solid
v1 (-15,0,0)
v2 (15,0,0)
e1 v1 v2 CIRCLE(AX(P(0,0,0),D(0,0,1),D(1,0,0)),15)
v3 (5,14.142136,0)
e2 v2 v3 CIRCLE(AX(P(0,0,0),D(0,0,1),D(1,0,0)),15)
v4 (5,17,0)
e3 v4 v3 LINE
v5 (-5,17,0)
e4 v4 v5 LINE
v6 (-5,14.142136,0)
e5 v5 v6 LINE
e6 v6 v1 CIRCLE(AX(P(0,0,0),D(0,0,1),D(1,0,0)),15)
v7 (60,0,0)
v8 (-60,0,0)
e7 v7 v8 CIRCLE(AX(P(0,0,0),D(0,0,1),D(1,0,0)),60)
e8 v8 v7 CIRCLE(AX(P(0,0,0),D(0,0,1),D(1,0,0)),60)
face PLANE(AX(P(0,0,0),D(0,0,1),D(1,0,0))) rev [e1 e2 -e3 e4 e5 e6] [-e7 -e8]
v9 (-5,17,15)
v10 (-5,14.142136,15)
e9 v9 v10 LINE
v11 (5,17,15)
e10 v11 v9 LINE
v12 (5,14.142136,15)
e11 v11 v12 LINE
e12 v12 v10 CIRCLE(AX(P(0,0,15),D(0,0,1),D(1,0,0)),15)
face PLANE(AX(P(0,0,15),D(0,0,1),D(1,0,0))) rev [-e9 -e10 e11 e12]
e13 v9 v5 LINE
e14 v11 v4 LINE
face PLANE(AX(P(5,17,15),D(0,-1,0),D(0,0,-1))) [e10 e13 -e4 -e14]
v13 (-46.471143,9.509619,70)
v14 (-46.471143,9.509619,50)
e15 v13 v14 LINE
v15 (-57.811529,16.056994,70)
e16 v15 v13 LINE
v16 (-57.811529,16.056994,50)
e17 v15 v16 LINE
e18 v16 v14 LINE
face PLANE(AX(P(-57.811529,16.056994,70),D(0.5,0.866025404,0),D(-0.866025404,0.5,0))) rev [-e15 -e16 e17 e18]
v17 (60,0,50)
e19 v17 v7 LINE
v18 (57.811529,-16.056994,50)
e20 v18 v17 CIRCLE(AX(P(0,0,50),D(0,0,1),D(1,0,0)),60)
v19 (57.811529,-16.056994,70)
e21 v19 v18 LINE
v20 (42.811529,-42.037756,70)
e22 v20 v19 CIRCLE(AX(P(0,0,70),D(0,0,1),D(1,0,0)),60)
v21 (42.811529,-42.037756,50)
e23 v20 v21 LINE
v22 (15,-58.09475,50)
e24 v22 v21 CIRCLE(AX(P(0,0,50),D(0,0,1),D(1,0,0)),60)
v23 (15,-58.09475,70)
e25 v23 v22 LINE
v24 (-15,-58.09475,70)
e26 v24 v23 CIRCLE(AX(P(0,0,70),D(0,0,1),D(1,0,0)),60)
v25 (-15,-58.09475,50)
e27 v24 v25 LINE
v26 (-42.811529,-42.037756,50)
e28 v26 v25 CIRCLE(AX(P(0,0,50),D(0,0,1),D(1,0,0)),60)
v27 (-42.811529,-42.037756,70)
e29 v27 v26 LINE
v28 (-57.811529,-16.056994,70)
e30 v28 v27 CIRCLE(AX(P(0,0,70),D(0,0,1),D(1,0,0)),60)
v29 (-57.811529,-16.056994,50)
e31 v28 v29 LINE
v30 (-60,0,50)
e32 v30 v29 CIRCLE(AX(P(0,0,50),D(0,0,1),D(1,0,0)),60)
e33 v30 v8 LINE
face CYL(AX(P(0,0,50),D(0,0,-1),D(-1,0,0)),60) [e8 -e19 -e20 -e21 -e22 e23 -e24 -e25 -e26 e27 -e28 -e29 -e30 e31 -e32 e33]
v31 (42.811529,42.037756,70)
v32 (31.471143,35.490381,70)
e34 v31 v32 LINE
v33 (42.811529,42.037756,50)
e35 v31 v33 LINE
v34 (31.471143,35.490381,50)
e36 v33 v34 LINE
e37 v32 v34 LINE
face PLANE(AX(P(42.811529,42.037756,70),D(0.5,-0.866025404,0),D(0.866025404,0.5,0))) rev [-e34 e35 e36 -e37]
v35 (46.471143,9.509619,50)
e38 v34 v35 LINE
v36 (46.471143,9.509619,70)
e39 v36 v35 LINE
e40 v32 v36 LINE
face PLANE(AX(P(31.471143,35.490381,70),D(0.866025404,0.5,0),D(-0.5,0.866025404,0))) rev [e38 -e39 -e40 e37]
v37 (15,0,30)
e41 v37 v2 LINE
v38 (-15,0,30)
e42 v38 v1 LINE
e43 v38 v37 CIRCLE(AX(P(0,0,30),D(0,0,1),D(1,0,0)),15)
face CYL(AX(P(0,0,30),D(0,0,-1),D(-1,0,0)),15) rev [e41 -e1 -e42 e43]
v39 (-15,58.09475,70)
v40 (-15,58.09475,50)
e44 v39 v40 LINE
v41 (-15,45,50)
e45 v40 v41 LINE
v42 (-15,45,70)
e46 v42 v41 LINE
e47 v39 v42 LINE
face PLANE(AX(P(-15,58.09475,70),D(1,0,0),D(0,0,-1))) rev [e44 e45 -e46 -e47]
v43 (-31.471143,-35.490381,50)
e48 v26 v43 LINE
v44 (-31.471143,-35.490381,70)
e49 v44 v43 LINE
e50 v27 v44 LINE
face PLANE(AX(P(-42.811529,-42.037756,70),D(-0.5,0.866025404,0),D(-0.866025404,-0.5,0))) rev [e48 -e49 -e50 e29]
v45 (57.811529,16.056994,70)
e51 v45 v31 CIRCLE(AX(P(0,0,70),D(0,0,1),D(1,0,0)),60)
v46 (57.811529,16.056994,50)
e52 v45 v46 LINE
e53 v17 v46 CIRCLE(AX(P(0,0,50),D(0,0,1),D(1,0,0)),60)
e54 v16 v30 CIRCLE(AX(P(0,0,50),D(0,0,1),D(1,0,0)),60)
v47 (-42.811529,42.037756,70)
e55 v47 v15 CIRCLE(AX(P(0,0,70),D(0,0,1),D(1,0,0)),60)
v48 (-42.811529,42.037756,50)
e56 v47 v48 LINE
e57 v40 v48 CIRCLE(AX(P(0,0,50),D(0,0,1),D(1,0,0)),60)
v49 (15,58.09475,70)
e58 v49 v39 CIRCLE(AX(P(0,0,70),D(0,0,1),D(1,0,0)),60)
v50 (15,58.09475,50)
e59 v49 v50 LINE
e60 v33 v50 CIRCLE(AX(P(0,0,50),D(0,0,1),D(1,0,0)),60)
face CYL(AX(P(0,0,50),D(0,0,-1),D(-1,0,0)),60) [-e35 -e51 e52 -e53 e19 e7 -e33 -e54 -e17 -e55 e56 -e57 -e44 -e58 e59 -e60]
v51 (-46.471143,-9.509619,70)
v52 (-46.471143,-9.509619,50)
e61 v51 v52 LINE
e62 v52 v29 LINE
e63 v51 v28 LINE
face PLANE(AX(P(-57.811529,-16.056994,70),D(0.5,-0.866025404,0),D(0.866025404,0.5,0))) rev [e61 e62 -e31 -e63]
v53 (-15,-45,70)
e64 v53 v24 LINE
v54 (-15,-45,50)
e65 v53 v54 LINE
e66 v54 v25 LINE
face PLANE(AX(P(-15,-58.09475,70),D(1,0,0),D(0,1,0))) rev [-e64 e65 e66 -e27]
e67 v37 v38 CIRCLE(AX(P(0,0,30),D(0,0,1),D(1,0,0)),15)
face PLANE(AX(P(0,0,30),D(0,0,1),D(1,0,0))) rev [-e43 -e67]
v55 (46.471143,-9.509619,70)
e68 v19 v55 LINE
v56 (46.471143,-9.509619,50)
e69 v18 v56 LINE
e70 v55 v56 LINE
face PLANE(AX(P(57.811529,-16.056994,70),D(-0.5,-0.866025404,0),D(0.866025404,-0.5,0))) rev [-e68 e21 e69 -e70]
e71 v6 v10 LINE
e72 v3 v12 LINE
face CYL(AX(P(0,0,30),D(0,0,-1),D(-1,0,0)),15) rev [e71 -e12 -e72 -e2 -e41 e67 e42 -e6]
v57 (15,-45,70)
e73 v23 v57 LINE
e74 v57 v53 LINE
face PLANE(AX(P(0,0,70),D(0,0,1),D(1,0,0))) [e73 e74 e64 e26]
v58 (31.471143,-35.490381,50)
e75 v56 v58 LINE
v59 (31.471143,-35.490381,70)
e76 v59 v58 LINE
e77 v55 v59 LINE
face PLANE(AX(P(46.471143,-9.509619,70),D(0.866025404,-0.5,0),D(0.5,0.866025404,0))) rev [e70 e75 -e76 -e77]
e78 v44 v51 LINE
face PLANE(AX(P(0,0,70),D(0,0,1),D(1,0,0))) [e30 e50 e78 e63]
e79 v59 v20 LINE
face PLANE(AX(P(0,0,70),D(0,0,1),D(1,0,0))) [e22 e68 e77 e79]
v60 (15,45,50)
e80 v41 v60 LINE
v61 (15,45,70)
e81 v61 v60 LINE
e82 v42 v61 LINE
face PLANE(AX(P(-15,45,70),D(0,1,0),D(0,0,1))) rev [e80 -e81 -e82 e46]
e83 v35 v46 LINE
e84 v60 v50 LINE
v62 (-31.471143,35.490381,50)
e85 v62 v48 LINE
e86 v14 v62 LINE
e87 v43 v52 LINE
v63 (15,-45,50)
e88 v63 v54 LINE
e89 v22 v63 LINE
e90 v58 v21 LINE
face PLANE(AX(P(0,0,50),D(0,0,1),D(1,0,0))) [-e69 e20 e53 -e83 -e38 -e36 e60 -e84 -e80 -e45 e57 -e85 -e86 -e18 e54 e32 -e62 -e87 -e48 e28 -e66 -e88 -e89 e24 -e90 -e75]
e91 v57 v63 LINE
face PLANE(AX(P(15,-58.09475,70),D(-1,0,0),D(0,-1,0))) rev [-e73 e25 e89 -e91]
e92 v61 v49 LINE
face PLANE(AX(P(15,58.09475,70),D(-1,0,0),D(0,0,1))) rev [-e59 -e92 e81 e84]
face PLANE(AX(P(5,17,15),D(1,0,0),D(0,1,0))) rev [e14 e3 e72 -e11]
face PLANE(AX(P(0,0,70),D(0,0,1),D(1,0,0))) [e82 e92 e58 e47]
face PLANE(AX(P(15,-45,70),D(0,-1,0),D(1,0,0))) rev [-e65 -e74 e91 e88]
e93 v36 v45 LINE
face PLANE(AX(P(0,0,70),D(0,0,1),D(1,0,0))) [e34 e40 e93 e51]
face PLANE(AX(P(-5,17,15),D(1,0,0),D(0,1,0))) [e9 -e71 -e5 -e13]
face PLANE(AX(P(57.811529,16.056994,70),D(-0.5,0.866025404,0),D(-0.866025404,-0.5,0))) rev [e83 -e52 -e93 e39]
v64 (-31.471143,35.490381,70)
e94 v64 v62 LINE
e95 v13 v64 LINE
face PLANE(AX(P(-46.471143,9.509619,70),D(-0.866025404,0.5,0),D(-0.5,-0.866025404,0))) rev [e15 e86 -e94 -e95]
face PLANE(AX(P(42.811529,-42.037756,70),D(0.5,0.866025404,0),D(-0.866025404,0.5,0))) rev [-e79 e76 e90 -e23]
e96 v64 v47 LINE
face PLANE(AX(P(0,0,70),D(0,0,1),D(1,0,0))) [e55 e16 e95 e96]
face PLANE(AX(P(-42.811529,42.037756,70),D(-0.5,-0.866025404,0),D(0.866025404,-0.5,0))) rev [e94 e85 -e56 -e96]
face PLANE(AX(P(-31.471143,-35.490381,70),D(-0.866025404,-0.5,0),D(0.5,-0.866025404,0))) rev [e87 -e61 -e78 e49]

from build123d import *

# Parameters (mm, degrees)
SKETCH_2_R          = 60
EXTRUDE_1_DEPTH     = 50
SKETCH_1_R          = 15
CUT_EXTRUDE_1_DEPTH = 30
EXTRUDE_2_DEPTH     = 20
SKETCH_5_W          = 10
SKETCH_5_H          = 6.88474508
CUT_EXTRUDE_2_DEPTH = 15


with BuildPart() as part:
    # 草图2 → 凸台-拉伸1 (new body)
    with BuildSketch(Plane.XY):
        Circle(SKETCH_2_R)
    extrude(amount=EXTRUDE_1_DEPTH)

    # 草图1 → 切除-拉伸1 (cut)
    with BuildSketch(Plane.XY):
        Circle(SKETCH_1_R)
    extrude(amount=CUT_EXTRUDE_1_DEPTH, mode=Mode.SUBTRACT)

    # 草图3 → 凸台-拉伸2 (add)
    with BuildSketch(Plane.XY.offset(50)):
        with BuildLine():
            Line((42.811529494, 42.037756153), (31.47114317, 35.490381057))
            Line((31.47114317, 35.490381057), (46.47114317, 9.509618943))
            Line((46.47114317, 9.509618943), (57.811529494, 16.05699404))
            ThreePointArc((57.811529494, 16.05699404), (51.961524227, 30), (42.811529494, 42.037756153))
        make_face()
        with BuildLine():
            Line((-15, 58.094750193), (-15, 45))
            Line((-15, 45), (15, 45))
            Line((15, 45), (15, 58.094750193))
            ThreePointArc((15, 58.094750193), (0, 60), (-15, 58.094750193))
        make_face()
        with BuildLine():
            Line((57.811529494, -16.05699404), (46.47114317, -9.509618943))
            Line((46.47114317, -9.509618943), (31.47114317, -35.490381057))
            Line((31.47114317, -35.490381057), (42.811529494, -42.037756153))
            ThreePointArc((42.811529494, -42.037756153), (51.961524227, -30), (57.811529494, -16.05699404))
        make_face()
        with BuildLine():
            Line((15, -58.094750193), (15, -45))
            Line((15, -45), (-15, -45))
            Line((-15, -45), (-15, -58.094750193))
            ThreePointArc((-15, -58.094750193), (0, -60), (15, -58.094750193))
        make_face()
        with BuildLine():
            Line((-42.811529494, -42.037756153), (-31.47114317, -35.490381057))
            Line((-31.47114317, -35.490381057), (-46.47114317, -9.509618943))
            Line((-46.47114317, -9.509618943), (-57.811529494, -16.05699404))
            ThreePointArc((-57.811529494, -16.05699404), (-51.961524227, -30), (-42.811529494, -42.037756153))
        make_face()
        with BuildLine():
            Line((-57.811529494, 16.05699404), (-46.47114317, 9.509618943))
            Line((-46.47114317, 9.509618943), (-31.47114317, 35.490381057))
            Line((-31.47114317, 35.490381057), (-42.811529494, 42.037756153))
            ThreePointArc((-42.811529494, 42.037756153), (-51.961524227, 30), (-57.811529494, 16.05699404))
        make_face()
    extrude(amount=EXTRUDE_2_DEPTH)

    # 草图5 → 切除-拉伸2 (cut)
    with BuildSketch(Plane(origin=(0, 0, 0), x_dir=(-1, 0, 0), z_dir=(0, 0, -1))):
        with Locations((0, 13.55762746)):
            Rectangle(SKETCH_5_W, SKETCH_5_H)
    extrude(amount=-CUT_EXTRUDE_2_DEPTH, mode=Mode.SUBTRACT)


solid = part.part
